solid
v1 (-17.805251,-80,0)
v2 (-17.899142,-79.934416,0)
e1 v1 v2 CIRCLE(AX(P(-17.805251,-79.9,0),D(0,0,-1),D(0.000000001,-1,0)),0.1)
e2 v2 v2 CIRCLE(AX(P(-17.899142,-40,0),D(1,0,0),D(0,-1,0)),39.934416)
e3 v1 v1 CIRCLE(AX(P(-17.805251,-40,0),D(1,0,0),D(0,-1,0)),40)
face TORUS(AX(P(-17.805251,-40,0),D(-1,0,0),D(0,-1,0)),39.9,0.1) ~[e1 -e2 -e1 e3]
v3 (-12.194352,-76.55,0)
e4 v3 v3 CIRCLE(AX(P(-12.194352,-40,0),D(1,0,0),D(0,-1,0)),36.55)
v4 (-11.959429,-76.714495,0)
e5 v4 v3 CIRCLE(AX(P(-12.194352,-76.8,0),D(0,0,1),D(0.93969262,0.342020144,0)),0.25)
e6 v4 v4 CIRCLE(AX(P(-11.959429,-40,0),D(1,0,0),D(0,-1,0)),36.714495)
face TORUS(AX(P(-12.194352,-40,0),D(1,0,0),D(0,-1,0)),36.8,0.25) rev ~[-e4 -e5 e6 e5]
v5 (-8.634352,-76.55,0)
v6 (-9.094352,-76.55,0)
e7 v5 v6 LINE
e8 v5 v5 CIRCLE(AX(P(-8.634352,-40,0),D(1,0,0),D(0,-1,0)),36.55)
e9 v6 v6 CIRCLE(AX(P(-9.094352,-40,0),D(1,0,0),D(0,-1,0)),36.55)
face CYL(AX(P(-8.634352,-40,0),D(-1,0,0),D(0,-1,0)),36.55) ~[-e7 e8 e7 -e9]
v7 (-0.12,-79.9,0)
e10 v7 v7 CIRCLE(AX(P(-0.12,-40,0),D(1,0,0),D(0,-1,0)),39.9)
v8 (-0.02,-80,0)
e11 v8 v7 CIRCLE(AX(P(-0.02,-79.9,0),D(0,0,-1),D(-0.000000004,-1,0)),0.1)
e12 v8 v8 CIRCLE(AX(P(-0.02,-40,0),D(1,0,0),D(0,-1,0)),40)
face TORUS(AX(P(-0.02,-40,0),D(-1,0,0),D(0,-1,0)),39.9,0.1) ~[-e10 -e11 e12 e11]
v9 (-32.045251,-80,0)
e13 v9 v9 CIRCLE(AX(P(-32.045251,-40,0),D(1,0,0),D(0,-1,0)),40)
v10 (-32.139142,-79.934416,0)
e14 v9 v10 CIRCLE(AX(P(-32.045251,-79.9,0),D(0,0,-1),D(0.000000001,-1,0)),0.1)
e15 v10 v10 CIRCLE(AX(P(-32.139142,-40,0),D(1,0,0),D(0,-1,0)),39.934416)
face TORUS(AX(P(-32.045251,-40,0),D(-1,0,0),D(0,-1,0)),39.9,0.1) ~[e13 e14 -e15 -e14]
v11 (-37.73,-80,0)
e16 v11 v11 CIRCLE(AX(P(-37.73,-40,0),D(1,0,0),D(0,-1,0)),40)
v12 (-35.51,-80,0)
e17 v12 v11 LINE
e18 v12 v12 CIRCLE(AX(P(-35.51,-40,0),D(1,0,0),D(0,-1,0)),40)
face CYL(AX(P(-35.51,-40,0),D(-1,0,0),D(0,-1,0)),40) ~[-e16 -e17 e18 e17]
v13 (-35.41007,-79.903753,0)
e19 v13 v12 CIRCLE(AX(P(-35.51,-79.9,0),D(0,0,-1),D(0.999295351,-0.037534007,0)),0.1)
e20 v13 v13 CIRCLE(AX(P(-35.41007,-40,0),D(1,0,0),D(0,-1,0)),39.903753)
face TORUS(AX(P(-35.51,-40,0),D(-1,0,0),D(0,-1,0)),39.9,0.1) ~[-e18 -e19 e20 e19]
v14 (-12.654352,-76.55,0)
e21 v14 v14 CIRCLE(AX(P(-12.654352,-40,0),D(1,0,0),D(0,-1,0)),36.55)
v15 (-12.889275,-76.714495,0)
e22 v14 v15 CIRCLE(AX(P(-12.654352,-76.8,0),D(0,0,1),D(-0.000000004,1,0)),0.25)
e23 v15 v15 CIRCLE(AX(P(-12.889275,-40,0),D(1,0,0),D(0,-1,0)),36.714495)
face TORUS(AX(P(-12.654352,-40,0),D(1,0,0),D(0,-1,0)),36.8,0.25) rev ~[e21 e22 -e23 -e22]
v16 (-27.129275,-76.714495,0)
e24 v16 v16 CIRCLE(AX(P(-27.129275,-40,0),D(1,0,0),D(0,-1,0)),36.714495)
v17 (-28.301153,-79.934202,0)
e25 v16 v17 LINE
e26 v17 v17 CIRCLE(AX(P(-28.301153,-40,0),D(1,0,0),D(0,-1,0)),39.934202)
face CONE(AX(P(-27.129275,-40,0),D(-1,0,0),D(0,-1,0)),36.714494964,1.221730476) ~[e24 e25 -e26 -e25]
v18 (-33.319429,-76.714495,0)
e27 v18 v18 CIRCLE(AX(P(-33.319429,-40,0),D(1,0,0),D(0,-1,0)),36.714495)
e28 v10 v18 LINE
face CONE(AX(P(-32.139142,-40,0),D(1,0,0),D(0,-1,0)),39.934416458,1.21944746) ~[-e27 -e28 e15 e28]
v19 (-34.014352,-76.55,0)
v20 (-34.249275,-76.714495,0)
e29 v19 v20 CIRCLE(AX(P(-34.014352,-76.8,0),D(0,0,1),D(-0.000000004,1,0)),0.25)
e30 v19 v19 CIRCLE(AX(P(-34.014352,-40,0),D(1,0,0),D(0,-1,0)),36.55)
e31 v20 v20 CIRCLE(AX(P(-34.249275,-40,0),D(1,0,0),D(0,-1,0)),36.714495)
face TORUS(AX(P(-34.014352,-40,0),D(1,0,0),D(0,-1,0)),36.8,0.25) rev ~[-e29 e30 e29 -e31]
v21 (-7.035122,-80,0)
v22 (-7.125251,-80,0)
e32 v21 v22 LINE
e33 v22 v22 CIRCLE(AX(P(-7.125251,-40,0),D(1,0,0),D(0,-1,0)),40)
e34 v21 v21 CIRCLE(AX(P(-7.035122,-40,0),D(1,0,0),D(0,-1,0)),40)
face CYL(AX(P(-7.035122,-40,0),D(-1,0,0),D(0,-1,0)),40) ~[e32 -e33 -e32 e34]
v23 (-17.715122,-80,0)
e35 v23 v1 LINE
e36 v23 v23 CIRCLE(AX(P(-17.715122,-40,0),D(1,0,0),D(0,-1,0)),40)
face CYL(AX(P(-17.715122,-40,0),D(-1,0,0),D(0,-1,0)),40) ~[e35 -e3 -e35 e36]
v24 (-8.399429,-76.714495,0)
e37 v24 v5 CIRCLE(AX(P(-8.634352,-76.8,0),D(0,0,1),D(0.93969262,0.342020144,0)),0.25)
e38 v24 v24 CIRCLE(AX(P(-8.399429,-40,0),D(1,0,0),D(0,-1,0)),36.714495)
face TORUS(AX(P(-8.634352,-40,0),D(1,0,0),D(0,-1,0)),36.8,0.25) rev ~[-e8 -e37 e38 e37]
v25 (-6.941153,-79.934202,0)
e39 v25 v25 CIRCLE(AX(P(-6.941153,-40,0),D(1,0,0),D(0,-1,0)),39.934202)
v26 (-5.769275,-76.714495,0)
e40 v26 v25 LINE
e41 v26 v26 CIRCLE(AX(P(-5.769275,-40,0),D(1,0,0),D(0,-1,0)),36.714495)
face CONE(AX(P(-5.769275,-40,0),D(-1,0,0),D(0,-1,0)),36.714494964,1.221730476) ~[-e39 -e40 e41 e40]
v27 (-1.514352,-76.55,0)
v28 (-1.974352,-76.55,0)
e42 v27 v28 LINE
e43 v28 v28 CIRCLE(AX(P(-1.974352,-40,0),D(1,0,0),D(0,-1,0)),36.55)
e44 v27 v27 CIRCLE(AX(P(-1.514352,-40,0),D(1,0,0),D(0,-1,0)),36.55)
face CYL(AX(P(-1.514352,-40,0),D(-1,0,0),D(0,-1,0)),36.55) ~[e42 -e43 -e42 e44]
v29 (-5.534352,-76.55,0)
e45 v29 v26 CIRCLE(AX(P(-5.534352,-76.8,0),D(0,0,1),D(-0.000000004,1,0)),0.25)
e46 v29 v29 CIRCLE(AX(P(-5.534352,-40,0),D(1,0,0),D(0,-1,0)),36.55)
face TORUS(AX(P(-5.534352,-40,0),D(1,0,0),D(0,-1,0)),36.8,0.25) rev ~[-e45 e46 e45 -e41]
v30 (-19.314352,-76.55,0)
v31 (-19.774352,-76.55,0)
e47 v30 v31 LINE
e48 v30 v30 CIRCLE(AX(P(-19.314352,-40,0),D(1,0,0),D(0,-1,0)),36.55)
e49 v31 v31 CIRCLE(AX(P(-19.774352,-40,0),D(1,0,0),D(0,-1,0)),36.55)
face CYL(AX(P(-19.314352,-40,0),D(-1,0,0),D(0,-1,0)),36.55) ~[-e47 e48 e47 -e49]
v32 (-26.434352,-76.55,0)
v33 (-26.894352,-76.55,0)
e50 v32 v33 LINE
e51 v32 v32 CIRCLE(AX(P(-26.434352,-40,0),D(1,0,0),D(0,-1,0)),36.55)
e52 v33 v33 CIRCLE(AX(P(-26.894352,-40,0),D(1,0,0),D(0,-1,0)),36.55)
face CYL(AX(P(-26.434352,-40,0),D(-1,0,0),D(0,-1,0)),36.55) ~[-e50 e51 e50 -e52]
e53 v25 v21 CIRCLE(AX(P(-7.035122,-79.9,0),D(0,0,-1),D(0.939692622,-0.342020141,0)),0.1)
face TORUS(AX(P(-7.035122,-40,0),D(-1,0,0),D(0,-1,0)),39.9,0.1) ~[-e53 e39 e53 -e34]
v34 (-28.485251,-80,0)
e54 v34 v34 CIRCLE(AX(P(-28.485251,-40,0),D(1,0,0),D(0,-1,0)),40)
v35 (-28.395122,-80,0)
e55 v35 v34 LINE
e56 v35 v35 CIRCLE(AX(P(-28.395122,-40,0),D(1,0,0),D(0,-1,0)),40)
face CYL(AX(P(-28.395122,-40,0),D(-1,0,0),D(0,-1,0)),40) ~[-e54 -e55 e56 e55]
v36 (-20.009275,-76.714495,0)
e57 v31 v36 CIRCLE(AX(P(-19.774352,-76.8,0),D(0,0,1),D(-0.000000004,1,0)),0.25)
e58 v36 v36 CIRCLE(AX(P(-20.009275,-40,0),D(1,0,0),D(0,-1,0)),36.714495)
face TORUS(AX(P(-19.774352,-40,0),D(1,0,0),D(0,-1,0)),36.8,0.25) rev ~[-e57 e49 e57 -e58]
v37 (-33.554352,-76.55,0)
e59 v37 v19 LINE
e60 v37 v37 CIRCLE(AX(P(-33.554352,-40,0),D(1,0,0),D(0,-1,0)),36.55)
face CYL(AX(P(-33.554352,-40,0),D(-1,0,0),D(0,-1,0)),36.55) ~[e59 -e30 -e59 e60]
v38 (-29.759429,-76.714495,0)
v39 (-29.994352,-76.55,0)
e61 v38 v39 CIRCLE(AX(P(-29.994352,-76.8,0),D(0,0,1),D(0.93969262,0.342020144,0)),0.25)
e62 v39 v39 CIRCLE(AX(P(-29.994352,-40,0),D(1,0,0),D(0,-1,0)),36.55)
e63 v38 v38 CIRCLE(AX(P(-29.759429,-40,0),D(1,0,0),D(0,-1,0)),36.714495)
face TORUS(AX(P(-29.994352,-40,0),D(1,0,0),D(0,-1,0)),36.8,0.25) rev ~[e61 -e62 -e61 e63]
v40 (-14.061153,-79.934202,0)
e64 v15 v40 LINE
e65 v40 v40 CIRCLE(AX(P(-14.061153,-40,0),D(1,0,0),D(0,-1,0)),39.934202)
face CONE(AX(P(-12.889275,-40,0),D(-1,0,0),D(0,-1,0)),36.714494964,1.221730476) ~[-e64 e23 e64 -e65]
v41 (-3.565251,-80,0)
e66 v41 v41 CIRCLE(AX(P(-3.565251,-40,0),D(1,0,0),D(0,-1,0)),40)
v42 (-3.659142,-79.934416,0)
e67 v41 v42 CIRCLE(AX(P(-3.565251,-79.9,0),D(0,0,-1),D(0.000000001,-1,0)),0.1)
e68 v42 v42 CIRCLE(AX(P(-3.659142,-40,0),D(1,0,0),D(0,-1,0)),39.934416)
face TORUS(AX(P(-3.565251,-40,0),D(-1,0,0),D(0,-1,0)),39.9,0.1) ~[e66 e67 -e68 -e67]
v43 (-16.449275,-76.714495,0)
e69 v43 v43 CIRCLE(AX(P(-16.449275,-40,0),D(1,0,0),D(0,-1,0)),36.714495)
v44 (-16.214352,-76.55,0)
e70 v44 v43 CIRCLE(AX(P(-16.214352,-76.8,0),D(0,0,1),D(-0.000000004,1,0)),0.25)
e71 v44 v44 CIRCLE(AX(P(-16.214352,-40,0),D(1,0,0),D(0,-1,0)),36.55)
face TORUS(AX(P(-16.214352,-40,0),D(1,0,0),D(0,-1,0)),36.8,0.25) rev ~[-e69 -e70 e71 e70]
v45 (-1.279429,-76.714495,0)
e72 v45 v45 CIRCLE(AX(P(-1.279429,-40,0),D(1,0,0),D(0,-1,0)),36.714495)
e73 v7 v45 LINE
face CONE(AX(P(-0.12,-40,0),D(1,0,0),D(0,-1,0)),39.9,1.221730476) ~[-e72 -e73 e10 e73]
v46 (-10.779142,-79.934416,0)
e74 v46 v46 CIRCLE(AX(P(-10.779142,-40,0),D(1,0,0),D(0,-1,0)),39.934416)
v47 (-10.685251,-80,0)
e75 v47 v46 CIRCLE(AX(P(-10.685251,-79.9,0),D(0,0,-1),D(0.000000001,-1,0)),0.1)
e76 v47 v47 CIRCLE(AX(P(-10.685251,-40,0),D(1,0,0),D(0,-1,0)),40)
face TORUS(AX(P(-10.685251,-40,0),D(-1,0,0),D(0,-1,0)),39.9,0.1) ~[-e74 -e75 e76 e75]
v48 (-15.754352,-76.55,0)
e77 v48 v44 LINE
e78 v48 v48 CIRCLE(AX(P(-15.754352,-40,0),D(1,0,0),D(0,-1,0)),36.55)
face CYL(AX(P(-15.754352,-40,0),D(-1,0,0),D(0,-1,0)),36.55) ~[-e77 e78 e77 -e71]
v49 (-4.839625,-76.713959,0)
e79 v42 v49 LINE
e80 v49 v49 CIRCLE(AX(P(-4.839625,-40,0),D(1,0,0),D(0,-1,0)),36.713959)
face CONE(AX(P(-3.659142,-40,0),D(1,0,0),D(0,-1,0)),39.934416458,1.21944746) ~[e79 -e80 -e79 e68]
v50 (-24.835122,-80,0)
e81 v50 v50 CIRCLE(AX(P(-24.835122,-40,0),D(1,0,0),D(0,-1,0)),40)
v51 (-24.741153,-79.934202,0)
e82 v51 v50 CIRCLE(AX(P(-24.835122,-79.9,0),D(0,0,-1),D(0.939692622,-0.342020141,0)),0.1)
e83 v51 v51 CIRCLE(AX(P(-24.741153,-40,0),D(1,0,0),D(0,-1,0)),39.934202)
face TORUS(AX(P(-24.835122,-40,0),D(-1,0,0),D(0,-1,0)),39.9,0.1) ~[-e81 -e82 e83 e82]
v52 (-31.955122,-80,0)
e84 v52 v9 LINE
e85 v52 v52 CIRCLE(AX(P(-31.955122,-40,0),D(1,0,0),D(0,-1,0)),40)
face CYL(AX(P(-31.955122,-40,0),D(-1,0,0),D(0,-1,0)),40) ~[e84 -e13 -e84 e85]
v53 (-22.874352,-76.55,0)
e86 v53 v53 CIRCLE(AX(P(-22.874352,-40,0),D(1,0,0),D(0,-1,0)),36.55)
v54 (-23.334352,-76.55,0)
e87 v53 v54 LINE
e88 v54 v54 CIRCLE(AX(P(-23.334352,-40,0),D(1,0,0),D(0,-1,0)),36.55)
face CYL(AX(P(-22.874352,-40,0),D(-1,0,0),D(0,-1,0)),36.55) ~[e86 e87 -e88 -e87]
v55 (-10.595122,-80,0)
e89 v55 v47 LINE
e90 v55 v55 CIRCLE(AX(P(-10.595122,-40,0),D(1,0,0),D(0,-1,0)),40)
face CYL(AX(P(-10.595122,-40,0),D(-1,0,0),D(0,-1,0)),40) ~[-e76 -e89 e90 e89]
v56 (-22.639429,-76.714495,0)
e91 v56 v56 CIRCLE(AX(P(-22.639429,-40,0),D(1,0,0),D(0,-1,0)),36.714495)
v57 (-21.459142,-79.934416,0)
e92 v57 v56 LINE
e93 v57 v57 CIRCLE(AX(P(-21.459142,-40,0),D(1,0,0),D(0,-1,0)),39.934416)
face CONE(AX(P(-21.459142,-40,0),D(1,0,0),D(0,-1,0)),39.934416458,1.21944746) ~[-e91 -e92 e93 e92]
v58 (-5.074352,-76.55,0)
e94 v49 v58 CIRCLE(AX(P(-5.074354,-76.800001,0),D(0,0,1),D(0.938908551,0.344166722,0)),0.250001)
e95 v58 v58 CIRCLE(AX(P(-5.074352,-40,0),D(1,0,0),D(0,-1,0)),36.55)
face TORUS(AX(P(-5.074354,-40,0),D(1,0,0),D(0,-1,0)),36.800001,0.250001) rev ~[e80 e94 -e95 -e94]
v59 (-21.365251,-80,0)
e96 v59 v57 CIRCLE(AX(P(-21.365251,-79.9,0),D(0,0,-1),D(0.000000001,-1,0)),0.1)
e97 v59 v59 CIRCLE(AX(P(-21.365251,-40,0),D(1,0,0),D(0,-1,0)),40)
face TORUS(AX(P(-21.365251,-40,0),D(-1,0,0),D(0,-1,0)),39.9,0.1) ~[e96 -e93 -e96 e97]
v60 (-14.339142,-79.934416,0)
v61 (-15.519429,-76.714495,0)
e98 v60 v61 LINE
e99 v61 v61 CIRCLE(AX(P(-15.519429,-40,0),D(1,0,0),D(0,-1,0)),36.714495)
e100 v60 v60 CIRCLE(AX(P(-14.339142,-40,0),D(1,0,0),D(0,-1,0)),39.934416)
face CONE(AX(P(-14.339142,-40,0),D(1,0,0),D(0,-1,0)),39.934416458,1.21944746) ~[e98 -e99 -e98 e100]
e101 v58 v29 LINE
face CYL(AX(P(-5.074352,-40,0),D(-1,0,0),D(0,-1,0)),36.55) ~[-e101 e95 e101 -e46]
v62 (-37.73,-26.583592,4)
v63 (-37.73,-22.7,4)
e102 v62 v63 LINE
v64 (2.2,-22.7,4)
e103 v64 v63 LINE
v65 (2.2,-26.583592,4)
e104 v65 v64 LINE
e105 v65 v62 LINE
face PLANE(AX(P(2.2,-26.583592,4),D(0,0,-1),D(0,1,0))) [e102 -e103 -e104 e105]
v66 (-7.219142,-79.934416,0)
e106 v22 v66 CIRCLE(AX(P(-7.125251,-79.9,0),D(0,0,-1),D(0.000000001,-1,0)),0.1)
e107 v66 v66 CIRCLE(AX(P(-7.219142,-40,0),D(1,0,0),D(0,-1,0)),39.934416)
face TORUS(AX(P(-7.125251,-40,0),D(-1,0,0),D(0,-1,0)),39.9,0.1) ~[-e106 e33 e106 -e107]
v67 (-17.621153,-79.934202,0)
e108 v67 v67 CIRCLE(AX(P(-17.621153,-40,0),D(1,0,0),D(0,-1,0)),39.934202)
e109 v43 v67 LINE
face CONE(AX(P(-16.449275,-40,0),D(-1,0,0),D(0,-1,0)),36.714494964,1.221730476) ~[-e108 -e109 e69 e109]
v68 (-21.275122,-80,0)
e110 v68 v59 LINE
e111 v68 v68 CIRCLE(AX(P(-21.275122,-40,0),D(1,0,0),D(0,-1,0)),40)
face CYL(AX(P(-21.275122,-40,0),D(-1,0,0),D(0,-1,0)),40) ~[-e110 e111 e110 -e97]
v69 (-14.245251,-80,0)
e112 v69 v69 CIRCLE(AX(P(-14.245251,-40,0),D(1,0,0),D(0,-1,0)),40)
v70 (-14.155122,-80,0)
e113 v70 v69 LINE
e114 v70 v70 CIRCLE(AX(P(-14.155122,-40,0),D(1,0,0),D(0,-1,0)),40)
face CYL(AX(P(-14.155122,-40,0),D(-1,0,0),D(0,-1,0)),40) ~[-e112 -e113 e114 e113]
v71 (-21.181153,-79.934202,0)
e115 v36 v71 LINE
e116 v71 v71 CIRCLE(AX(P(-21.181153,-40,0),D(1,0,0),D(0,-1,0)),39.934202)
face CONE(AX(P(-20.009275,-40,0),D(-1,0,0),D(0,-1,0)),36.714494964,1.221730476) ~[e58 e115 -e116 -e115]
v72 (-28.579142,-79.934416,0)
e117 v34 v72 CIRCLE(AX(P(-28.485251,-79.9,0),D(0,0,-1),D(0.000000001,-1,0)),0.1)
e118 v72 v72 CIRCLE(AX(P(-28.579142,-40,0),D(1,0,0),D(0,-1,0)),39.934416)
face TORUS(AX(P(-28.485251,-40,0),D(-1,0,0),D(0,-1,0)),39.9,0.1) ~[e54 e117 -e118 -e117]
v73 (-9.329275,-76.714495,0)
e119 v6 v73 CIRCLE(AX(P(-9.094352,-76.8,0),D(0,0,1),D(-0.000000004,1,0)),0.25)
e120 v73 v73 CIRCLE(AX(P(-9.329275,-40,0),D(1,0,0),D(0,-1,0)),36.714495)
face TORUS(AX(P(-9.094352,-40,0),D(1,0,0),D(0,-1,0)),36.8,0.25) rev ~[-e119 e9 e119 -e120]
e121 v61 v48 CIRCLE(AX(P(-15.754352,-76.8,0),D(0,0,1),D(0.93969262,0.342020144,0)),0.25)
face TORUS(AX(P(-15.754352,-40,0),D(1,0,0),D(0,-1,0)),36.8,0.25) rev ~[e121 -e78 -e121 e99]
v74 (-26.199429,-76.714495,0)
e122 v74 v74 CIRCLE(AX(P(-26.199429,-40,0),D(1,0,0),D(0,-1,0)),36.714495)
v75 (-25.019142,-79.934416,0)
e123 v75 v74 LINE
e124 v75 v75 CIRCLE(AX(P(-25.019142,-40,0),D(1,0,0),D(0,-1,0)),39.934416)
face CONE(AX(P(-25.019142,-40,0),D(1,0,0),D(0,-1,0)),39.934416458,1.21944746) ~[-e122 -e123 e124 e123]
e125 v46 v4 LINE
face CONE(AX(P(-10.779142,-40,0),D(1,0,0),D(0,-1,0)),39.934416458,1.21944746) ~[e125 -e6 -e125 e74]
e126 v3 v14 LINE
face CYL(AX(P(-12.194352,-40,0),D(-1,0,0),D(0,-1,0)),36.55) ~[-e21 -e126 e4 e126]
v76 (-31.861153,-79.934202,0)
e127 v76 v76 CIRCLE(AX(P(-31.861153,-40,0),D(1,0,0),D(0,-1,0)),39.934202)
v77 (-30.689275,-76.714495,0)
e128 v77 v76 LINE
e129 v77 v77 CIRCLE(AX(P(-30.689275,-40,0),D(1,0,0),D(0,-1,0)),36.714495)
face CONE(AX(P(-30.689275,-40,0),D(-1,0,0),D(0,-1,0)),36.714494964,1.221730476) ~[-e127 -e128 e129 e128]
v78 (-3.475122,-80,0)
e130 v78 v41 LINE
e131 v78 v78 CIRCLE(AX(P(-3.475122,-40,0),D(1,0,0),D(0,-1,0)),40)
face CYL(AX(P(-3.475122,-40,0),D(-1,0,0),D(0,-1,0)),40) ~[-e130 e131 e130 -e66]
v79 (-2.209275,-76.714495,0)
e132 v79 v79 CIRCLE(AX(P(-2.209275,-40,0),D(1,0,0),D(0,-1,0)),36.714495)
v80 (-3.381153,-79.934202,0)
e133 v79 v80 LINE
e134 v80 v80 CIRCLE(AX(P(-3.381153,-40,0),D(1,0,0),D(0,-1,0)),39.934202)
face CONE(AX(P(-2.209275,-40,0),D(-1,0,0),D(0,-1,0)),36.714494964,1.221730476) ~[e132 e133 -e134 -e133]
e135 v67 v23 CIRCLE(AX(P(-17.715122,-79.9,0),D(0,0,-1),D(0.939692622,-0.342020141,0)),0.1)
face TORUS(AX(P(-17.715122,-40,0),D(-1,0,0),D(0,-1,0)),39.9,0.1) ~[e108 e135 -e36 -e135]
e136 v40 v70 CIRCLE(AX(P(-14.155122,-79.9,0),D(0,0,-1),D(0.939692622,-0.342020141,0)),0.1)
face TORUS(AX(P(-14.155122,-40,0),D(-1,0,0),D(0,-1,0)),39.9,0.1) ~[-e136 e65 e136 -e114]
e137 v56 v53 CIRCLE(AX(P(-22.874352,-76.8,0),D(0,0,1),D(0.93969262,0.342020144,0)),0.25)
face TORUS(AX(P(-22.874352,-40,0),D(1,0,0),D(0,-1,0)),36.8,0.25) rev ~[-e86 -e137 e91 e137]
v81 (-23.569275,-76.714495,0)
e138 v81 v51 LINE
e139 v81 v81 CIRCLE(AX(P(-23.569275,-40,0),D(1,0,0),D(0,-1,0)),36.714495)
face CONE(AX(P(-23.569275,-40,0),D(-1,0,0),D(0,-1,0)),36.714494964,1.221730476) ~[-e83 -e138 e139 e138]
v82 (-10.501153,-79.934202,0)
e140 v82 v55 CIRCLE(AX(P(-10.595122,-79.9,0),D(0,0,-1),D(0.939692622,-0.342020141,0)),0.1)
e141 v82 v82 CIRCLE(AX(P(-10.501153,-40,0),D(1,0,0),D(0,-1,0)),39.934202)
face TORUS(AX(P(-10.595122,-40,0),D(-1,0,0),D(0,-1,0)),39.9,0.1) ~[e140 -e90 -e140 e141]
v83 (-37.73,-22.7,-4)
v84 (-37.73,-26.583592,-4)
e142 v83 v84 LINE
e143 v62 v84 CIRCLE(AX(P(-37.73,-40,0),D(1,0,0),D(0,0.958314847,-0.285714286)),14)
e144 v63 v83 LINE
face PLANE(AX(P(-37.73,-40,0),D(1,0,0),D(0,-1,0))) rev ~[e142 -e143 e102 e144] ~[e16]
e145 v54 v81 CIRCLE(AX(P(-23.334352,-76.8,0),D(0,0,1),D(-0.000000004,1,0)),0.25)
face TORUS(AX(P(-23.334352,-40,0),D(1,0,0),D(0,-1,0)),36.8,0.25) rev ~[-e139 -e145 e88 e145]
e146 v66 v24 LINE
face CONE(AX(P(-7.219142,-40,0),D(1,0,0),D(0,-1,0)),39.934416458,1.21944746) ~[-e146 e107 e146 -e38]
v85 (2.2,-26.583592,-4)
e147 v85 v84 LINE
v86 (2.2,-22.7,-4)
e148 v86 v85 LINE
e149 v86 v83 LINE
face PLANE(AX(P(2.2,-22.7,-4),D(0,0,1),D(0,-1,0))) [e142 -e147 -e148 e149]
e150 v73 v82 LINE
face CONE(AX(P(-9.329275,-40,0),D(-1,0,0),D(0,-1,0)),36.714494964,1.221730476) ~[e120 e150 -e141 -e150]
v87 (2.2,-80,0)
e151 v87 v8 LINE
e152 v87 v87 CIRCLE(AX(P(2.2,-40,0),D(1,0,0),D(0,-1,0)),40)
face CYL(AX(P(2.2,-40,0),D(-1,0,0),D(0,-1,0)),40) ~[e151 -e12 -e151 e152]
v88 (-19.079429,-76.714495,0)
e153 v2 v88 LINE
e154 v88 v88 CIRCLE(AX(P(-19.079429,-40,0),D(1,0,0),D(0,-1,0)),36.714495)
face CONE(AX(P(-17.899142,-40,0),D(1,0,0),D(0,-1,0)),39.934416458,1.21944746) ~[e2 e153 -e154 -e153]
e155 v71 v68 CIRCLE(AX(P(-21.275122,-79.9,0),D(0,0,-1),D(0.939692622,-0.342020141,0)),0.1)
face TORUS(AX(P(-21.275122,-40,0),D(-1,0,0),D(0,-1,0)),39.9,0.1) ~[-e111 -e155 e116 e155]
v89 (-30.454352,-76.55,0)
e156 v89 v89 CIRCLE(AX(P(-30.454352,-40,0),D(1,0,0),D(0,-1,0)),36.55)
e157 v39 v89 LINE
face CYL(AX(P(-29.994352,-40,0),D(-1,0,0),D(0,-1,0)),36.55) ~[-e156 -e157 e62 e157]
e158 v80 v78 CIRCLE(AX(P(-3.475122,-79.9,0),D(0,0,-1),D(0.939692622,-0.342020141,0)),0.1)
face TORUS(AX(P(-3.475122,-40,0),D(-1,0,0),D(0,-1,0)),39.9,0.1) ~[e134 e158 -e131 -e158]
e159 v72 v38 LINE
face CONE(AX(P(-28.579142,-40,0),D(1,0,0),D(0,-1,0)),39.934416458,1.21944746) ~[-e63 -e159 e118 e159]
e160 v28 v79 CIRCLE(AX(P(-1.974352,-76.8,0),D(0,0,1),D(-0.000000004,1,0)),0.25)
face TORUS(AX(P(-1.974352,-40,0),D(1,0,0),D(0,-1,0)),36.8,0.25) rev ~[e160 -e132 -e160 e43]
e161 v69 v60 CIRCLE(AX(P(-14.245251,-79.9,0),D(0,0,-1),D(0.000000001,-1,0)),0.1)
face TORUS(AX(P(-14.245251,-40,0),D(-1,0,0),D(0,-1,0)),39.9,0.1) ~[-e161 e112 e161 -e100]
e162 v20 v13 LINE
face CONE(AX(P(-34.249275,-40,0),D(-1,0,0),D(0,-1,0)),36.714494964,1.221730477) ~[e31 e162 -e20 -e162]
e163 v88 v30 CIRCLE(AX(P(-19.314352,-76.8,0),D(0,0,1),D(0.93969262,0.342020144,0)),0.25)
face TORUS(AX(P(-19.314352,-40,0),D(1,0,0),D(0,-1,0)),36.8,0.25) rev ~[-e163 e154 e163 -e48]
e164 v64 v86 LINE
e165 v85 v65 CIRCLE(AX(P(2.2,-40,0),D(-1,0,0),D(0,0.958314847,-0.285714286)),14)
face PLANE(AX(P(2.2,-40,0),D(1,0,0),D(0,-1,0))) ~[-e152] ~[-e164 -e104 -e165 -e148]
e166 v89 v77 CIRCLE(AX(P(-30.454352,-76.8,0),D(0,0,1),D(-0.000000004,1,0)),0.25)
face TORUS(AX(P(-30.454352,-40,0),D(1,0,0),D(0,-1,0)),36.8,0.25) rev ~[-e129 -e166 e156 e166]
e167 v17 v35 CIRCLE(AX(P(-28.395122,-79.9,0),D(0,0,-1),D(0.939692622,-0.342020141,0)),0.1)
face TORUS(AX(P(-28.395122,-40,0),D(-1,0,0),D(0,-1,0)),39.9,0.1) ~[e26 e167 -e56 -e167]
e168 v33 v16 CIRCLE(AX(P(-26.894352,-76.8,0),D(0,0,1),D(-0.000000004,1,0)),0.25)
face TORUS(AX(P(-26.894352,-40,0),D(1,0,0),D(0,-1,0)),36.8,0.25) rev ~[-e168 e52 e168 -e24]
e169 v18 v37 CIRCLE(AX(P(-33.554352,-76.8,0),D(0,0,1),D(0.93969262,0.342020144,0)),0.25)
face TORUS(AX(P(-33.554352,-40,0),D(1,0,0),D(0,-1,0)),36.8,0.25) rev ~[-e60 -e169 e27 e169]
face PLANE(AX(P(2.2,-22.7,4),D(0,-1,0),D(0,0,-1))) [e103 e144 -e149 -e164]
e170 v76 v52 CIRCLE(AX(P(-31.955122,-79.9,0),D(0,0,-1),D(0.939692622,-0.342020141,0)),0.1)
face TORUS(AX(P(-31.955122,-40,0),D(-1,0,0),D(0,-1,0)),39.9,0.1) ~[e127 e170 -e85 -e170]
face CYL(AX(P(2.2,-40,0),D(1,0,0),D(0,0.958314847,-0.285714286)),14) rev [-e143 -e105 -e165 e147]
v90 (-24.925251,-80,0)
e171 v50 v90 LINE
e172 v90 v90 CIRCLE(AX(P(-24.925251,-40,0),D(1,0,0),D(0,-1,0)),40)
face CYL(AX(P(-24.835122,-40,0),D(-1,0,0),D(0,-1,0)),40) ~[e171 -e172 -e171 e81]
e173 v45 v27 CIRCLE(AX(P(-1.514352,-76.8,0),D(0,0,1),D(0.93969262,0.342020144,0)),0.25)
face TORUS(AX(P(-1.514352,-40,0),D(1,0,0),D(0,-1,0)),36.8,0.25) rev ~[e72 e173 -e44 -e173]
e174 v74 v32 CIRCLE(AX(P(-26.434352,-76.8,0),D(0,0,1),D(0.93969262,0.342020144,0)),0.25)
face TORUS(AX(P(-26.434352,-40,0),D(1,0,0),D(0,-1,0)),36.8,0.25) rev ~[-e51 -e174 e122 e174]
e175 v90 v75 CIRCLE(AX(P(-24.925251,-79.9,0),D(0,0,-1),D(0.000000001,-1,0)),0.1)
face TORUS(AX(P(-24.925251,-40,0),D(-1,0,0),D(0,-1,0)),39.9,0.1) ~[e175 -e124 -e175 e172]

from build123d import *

# Parameters (mm, degrees)
CUT_EXTRUDE1_DEPTH = 98.951033297


with BuildPart() as part:
    # Sketch1 → Revolve1 (revolve)
    with BuildSketch(Plane.XY, mode=Mode.PRIVATE) as revolve1_sk:
        with BuildLine():
            ThreePointArc((-0.02, 0), (-0.090710678, -0.029289322), (-0.12, -0.1))
            Line((-0.12, -0.1), (-1.279429014, -3.285505036))
            ThreePointArc((-1.279429014, -3.285505036), (-1.37095806, -3.404788011), (-1.514352169, -3.45))
            Line((-1.514352169, -3.45), (-1.974352169, -3.45))
            ThreePointArc((-1.974352169, -3.45), (-2.117746278, -3.404788011), (-2.209275325, -3.285505036))
            Line((-2.209275325, -3.285505036), (-3.381152854, -0.065797986))
            ThreePointArc((-3.381152854, -0.065797986), (-3.417764472, -0.018084796), (-3.475122116, 0))
            Line((-3.475122116, 0), (-3.56525059, 0))
            ThreePointArc((-3.56525059, 0), (-3.62251469, -0.018019375), (-3.659141524, -0.065583542))
            Line((-3.659141524, -0.065583542), (-4.839625447, -3.286040922))
            ThreePointArc((-4.839625447, -3.286040922), (-4.931192378, -3.404951088), (-5.074352169, -3.45))
            Line((-5.074352169, -3.45), (-5.534352169, -3.45))
            ThreePointArc((-5.534352169, -3.45), (-5.677746278, -3.404788011), (-5.769275325, -3.285505036))
            Line((-5.769275325, -3.285505036), (-6.941152854, -0.065797986))
            ThreePointArc((-6.941152854, -0.065797986), (-6.977764472, -0.018084796), (-7.035122116, 0))
            Line((-7.035122116, 0), (-7.12525059, 0))
            ThreePointArc((-7.12525059, 0), (-7.18251469, -0.018019375), (-7.219141524, -0.065583542))
            Line((-7.219141524, -0.065583542), (-8.399429014, -3.285505036))
            ThreePointArc((-8.399429014, -3.285505036), (-8.49095806, -3.404788011), (-8.634352169, -3.45))
            Line((-8.634352169, -3.45), (-9.094352169, -3.45))
            ThreePointArc((-9.094352169, -3.45), (-9.237746278, -3.404788011), (-9.329275325, -3.285505036))
            Line((-9.329275325, -3.285505036), (-10.501152854, -0.065797986))
            ThreePointArc((-10.501152854, -0.065797986), (-10.537764472, -0.018084796), (-10.595122116, 0))
            Line((-10.595122116, 0), (-10.68525059, 0))
            ThreePointArc((-10.68525059, 0), (-10.74251469, -0.018019375), (-10.779141524, -0.065583542))
            Line((-10.779141524, -0.065583542), (-11.959429014, -3.285505036))
            ThreePointArc((-11.959429014, -3.285505036), (-12.05095806, -3.404788011), (-12.194352169, -3.45))
            Line((-12.194352169, -3.45), (-12.654352169, -3.45))
            ThreePointArc((-12.654352169, -3.45), (-12.797746278, -3.404788011), (-12.889275325, -3.285505036))
            Line((-12.889275325, -3.285505036), (-14.061152854, -0.065797986))
            ThreePointArc((-14.061152854, -0.065797986), (-14.097764472, -0.018084796), (-14.155122116, 0))
            Line((-14.155122116, 0), (-14.24525059, 0))
            ThreePointArc((-14.24525059, 0), (-14.30251469, -0.018019375), (-14.339141524, -0.065583542))
            Line((-14.339141524, -0.065583542), (-15.519429014, -3.285505036))
            ThreePointArc((-15.519429014, -3.285505036), (-15.61095806, -3.404788011), (-15.754352169, -3.45))
            Line((-15.754352169, -3.45), (-16.214352169, -3.45))
            ThreePointArc((-16.214352169, -3.45), (-16.357746278, -3.404788011), (-16.449275325, -3.285505036))
            Line((-16.449275325, -3.285505036), (-17.621152854, -0.065797986))
            ThreePointArc((-17.621152854, -0.065797986), (-17.657764472, -0.018084796), (-17.715122116, 0))
            Line((-17.715122116, 0), (-17.80525059, 0))
            ThreePointArc((-17.80525059, 0), (-17.86251469, -0.018019375), (-17.899141524, -0.065583542))
            Line((-17.899141524, -0.065583542), (-19.079429014, -3.285505036))
            ThreePointArc((-19.079429014, -3.285505036), (-19.17095806, -3.404788011), (-19.314352169, -3.45))
            Line((-19.314352169, -3.45), (-19.774352169, -3.45))
            ThreePointArc((-19.774352169, -3.45), (-19.917746278, -3.404788011), (-20.009275325, -3.285505036))
            Line((-20.009275325, -3.285505036), (-21.181152854, -0.065797986))
            ThreePointArc((-21.181152854, -0.065797986), (-21.217764472, -0.018084796), (-21.275122116, 0))
            Line((-21.275122116, 0), (-21.36525059, 0))
            ThreePointArc((-21.36525059, 0), (-21.42251469, -0.018019375), (-21.459141524, -0.065583542))
            Line((-21.459141524, -0.065583542), (-22.639429014, -3.285505036))
            ThreePointArc((-22.639429014, -3.285505036), (-22.73095806, -3.404788011), (-22.874352169, -3.45))
            Line((-22.874352169, -3.45), (-23.334352169, -3.45))
            ThreePointArc((-23.334352169, -3.45), (-23.477746278, -3.404788011), (-23.569275325, -3.285505036))
            Line((-23.569275325, -3.285505036), (-24.741152854, -0.065797986))
            ThreePointArc((-24.741152854, -0.065797986), (-24.777764472, -0.018084796), (-24.835122116, 0))
            Line((-24.835122116, 0), (-24.92525059, 0))
            ThreePointArc((-24.92525059, 0), (-24.98251469, -0.018019375), (-25.019141524, -0.065583542))
            Line((-25.019141524, -0.065583542), (-26.199429014, -3.285505036))
            ThreePointArc((-26.199429014, -3.285505036), (-26.29095806, -3.404788011), (-26.434352169, -3.45))
            Line((-26.434352169, -3.45), (-26.894352169, -3.45))
            ThreePointArc((-26.894352169, -3.45), (-27.037746278, -3.404788011), (-27.129275325, -3.285505036))
            Line((-27.129275325, -3.285505036), (-28.301152854, -0.065797986))
            ThreePointArc((-28.301152854, -0.065797986), (-28.337764472, -0.018084796), (-28.395122116, 0))
            Line((-28.395122116, 0), (-28.48525059, 0))
            ThreePointArc((-28.48525059, 0), (-28.54251469, -0.018019375), (-28.579141524, -0.065583542))
            Line((-28.579141524, -0.065583542), (-29.759429014, -3.285505036))
            ThreePointArc((-29.759429014, -3.285505036), (-29.85095806, -3.404788011), (-29.994352169, -3.45))
            Line((-29.994352169, -3.45), (-30.454352169, -3.45))
            ThreePointArc((-30.454352169, -3.45), (-30.597746278, -3.404788011), (-30.689275325, -3.285505036))
            Line((-30.689275325, -3.285505036), (-31.861152854, -0.065797986))
            ThreePointArc((-31.861152854, -0.065797986), (-31.897764472, -0.018084796), (-31.955122116, 0))
            Line((-31.955122116, 0), (-32.04525059, 0))
            ThreePointArc((-32.04525059, 0), (-32.10251469, -0.018019375), (-32.139141524, -0.065583542))
            Line((-32.139141524, -0.065583542), (-33.319429014, -3.285505036))
            ThreePointArc((-33.319429014, -3.285505036), (-33.41095806, -3.404788011), (-33.554352169, -3.45))
            Line((-33.554352169, -3.45), (-34.014352169, -3.45))
            ThreePointArc((-34.014352169, -3.45), (-34.157746278, -3.404788011), (-34.249275325, -3.285505036))
            Line((-34.249275325, -3.285505036), (-35.410070465, -0.096246599))
            ThreePointArc((-35.410070465, -0.096246599), (-35.440629041, -0.027974518), (-35.51, 0))
            Line((-35.51, 0), (-35.515122116, 0))
            Line((-35.515122116, 0), (-35.60525059, 0))
            Line((-35.60525059, 0), (-37.73, 0))
            Line((-37.73, 0), (-37.73, -40))
            Line((-37.73, -40), (2.2, -40))
            Line((2.2, -40), (2.2, 0))
            Line((2.2, 0), (-0.02, 0))
        make_face()
    revolve(revolve1_sk.sketch.rotate(Axis((-37.73, -40, 0), (1, 0, 0)), 180), axis=Axis((-37.73, -40, 0), (1, 0, 0)))

    # Sketch2 → Cut-Extrude1 (cut, through all)
    with BuildSketch(Plane(origin=(2.2, 0, 0), x_dir=(0, 0, -1), z_dir=(1, 0, 0))):
        with BuildLine():
            Line((-4, -22.7), (4, -22.7))
            Line((4, -22.7), (4, -26.583592135))
            ThreePointArc((4, -26.583592135), (0, -54), (-4, -26.583592135))
            Line((-4, -26.583592135), (-4, -22.7))
        make_face()
    extrude(amount=-CUT_EXTRUDE1_DEPTH, mode=Mode.SUBTRACT)


solid = part.part
